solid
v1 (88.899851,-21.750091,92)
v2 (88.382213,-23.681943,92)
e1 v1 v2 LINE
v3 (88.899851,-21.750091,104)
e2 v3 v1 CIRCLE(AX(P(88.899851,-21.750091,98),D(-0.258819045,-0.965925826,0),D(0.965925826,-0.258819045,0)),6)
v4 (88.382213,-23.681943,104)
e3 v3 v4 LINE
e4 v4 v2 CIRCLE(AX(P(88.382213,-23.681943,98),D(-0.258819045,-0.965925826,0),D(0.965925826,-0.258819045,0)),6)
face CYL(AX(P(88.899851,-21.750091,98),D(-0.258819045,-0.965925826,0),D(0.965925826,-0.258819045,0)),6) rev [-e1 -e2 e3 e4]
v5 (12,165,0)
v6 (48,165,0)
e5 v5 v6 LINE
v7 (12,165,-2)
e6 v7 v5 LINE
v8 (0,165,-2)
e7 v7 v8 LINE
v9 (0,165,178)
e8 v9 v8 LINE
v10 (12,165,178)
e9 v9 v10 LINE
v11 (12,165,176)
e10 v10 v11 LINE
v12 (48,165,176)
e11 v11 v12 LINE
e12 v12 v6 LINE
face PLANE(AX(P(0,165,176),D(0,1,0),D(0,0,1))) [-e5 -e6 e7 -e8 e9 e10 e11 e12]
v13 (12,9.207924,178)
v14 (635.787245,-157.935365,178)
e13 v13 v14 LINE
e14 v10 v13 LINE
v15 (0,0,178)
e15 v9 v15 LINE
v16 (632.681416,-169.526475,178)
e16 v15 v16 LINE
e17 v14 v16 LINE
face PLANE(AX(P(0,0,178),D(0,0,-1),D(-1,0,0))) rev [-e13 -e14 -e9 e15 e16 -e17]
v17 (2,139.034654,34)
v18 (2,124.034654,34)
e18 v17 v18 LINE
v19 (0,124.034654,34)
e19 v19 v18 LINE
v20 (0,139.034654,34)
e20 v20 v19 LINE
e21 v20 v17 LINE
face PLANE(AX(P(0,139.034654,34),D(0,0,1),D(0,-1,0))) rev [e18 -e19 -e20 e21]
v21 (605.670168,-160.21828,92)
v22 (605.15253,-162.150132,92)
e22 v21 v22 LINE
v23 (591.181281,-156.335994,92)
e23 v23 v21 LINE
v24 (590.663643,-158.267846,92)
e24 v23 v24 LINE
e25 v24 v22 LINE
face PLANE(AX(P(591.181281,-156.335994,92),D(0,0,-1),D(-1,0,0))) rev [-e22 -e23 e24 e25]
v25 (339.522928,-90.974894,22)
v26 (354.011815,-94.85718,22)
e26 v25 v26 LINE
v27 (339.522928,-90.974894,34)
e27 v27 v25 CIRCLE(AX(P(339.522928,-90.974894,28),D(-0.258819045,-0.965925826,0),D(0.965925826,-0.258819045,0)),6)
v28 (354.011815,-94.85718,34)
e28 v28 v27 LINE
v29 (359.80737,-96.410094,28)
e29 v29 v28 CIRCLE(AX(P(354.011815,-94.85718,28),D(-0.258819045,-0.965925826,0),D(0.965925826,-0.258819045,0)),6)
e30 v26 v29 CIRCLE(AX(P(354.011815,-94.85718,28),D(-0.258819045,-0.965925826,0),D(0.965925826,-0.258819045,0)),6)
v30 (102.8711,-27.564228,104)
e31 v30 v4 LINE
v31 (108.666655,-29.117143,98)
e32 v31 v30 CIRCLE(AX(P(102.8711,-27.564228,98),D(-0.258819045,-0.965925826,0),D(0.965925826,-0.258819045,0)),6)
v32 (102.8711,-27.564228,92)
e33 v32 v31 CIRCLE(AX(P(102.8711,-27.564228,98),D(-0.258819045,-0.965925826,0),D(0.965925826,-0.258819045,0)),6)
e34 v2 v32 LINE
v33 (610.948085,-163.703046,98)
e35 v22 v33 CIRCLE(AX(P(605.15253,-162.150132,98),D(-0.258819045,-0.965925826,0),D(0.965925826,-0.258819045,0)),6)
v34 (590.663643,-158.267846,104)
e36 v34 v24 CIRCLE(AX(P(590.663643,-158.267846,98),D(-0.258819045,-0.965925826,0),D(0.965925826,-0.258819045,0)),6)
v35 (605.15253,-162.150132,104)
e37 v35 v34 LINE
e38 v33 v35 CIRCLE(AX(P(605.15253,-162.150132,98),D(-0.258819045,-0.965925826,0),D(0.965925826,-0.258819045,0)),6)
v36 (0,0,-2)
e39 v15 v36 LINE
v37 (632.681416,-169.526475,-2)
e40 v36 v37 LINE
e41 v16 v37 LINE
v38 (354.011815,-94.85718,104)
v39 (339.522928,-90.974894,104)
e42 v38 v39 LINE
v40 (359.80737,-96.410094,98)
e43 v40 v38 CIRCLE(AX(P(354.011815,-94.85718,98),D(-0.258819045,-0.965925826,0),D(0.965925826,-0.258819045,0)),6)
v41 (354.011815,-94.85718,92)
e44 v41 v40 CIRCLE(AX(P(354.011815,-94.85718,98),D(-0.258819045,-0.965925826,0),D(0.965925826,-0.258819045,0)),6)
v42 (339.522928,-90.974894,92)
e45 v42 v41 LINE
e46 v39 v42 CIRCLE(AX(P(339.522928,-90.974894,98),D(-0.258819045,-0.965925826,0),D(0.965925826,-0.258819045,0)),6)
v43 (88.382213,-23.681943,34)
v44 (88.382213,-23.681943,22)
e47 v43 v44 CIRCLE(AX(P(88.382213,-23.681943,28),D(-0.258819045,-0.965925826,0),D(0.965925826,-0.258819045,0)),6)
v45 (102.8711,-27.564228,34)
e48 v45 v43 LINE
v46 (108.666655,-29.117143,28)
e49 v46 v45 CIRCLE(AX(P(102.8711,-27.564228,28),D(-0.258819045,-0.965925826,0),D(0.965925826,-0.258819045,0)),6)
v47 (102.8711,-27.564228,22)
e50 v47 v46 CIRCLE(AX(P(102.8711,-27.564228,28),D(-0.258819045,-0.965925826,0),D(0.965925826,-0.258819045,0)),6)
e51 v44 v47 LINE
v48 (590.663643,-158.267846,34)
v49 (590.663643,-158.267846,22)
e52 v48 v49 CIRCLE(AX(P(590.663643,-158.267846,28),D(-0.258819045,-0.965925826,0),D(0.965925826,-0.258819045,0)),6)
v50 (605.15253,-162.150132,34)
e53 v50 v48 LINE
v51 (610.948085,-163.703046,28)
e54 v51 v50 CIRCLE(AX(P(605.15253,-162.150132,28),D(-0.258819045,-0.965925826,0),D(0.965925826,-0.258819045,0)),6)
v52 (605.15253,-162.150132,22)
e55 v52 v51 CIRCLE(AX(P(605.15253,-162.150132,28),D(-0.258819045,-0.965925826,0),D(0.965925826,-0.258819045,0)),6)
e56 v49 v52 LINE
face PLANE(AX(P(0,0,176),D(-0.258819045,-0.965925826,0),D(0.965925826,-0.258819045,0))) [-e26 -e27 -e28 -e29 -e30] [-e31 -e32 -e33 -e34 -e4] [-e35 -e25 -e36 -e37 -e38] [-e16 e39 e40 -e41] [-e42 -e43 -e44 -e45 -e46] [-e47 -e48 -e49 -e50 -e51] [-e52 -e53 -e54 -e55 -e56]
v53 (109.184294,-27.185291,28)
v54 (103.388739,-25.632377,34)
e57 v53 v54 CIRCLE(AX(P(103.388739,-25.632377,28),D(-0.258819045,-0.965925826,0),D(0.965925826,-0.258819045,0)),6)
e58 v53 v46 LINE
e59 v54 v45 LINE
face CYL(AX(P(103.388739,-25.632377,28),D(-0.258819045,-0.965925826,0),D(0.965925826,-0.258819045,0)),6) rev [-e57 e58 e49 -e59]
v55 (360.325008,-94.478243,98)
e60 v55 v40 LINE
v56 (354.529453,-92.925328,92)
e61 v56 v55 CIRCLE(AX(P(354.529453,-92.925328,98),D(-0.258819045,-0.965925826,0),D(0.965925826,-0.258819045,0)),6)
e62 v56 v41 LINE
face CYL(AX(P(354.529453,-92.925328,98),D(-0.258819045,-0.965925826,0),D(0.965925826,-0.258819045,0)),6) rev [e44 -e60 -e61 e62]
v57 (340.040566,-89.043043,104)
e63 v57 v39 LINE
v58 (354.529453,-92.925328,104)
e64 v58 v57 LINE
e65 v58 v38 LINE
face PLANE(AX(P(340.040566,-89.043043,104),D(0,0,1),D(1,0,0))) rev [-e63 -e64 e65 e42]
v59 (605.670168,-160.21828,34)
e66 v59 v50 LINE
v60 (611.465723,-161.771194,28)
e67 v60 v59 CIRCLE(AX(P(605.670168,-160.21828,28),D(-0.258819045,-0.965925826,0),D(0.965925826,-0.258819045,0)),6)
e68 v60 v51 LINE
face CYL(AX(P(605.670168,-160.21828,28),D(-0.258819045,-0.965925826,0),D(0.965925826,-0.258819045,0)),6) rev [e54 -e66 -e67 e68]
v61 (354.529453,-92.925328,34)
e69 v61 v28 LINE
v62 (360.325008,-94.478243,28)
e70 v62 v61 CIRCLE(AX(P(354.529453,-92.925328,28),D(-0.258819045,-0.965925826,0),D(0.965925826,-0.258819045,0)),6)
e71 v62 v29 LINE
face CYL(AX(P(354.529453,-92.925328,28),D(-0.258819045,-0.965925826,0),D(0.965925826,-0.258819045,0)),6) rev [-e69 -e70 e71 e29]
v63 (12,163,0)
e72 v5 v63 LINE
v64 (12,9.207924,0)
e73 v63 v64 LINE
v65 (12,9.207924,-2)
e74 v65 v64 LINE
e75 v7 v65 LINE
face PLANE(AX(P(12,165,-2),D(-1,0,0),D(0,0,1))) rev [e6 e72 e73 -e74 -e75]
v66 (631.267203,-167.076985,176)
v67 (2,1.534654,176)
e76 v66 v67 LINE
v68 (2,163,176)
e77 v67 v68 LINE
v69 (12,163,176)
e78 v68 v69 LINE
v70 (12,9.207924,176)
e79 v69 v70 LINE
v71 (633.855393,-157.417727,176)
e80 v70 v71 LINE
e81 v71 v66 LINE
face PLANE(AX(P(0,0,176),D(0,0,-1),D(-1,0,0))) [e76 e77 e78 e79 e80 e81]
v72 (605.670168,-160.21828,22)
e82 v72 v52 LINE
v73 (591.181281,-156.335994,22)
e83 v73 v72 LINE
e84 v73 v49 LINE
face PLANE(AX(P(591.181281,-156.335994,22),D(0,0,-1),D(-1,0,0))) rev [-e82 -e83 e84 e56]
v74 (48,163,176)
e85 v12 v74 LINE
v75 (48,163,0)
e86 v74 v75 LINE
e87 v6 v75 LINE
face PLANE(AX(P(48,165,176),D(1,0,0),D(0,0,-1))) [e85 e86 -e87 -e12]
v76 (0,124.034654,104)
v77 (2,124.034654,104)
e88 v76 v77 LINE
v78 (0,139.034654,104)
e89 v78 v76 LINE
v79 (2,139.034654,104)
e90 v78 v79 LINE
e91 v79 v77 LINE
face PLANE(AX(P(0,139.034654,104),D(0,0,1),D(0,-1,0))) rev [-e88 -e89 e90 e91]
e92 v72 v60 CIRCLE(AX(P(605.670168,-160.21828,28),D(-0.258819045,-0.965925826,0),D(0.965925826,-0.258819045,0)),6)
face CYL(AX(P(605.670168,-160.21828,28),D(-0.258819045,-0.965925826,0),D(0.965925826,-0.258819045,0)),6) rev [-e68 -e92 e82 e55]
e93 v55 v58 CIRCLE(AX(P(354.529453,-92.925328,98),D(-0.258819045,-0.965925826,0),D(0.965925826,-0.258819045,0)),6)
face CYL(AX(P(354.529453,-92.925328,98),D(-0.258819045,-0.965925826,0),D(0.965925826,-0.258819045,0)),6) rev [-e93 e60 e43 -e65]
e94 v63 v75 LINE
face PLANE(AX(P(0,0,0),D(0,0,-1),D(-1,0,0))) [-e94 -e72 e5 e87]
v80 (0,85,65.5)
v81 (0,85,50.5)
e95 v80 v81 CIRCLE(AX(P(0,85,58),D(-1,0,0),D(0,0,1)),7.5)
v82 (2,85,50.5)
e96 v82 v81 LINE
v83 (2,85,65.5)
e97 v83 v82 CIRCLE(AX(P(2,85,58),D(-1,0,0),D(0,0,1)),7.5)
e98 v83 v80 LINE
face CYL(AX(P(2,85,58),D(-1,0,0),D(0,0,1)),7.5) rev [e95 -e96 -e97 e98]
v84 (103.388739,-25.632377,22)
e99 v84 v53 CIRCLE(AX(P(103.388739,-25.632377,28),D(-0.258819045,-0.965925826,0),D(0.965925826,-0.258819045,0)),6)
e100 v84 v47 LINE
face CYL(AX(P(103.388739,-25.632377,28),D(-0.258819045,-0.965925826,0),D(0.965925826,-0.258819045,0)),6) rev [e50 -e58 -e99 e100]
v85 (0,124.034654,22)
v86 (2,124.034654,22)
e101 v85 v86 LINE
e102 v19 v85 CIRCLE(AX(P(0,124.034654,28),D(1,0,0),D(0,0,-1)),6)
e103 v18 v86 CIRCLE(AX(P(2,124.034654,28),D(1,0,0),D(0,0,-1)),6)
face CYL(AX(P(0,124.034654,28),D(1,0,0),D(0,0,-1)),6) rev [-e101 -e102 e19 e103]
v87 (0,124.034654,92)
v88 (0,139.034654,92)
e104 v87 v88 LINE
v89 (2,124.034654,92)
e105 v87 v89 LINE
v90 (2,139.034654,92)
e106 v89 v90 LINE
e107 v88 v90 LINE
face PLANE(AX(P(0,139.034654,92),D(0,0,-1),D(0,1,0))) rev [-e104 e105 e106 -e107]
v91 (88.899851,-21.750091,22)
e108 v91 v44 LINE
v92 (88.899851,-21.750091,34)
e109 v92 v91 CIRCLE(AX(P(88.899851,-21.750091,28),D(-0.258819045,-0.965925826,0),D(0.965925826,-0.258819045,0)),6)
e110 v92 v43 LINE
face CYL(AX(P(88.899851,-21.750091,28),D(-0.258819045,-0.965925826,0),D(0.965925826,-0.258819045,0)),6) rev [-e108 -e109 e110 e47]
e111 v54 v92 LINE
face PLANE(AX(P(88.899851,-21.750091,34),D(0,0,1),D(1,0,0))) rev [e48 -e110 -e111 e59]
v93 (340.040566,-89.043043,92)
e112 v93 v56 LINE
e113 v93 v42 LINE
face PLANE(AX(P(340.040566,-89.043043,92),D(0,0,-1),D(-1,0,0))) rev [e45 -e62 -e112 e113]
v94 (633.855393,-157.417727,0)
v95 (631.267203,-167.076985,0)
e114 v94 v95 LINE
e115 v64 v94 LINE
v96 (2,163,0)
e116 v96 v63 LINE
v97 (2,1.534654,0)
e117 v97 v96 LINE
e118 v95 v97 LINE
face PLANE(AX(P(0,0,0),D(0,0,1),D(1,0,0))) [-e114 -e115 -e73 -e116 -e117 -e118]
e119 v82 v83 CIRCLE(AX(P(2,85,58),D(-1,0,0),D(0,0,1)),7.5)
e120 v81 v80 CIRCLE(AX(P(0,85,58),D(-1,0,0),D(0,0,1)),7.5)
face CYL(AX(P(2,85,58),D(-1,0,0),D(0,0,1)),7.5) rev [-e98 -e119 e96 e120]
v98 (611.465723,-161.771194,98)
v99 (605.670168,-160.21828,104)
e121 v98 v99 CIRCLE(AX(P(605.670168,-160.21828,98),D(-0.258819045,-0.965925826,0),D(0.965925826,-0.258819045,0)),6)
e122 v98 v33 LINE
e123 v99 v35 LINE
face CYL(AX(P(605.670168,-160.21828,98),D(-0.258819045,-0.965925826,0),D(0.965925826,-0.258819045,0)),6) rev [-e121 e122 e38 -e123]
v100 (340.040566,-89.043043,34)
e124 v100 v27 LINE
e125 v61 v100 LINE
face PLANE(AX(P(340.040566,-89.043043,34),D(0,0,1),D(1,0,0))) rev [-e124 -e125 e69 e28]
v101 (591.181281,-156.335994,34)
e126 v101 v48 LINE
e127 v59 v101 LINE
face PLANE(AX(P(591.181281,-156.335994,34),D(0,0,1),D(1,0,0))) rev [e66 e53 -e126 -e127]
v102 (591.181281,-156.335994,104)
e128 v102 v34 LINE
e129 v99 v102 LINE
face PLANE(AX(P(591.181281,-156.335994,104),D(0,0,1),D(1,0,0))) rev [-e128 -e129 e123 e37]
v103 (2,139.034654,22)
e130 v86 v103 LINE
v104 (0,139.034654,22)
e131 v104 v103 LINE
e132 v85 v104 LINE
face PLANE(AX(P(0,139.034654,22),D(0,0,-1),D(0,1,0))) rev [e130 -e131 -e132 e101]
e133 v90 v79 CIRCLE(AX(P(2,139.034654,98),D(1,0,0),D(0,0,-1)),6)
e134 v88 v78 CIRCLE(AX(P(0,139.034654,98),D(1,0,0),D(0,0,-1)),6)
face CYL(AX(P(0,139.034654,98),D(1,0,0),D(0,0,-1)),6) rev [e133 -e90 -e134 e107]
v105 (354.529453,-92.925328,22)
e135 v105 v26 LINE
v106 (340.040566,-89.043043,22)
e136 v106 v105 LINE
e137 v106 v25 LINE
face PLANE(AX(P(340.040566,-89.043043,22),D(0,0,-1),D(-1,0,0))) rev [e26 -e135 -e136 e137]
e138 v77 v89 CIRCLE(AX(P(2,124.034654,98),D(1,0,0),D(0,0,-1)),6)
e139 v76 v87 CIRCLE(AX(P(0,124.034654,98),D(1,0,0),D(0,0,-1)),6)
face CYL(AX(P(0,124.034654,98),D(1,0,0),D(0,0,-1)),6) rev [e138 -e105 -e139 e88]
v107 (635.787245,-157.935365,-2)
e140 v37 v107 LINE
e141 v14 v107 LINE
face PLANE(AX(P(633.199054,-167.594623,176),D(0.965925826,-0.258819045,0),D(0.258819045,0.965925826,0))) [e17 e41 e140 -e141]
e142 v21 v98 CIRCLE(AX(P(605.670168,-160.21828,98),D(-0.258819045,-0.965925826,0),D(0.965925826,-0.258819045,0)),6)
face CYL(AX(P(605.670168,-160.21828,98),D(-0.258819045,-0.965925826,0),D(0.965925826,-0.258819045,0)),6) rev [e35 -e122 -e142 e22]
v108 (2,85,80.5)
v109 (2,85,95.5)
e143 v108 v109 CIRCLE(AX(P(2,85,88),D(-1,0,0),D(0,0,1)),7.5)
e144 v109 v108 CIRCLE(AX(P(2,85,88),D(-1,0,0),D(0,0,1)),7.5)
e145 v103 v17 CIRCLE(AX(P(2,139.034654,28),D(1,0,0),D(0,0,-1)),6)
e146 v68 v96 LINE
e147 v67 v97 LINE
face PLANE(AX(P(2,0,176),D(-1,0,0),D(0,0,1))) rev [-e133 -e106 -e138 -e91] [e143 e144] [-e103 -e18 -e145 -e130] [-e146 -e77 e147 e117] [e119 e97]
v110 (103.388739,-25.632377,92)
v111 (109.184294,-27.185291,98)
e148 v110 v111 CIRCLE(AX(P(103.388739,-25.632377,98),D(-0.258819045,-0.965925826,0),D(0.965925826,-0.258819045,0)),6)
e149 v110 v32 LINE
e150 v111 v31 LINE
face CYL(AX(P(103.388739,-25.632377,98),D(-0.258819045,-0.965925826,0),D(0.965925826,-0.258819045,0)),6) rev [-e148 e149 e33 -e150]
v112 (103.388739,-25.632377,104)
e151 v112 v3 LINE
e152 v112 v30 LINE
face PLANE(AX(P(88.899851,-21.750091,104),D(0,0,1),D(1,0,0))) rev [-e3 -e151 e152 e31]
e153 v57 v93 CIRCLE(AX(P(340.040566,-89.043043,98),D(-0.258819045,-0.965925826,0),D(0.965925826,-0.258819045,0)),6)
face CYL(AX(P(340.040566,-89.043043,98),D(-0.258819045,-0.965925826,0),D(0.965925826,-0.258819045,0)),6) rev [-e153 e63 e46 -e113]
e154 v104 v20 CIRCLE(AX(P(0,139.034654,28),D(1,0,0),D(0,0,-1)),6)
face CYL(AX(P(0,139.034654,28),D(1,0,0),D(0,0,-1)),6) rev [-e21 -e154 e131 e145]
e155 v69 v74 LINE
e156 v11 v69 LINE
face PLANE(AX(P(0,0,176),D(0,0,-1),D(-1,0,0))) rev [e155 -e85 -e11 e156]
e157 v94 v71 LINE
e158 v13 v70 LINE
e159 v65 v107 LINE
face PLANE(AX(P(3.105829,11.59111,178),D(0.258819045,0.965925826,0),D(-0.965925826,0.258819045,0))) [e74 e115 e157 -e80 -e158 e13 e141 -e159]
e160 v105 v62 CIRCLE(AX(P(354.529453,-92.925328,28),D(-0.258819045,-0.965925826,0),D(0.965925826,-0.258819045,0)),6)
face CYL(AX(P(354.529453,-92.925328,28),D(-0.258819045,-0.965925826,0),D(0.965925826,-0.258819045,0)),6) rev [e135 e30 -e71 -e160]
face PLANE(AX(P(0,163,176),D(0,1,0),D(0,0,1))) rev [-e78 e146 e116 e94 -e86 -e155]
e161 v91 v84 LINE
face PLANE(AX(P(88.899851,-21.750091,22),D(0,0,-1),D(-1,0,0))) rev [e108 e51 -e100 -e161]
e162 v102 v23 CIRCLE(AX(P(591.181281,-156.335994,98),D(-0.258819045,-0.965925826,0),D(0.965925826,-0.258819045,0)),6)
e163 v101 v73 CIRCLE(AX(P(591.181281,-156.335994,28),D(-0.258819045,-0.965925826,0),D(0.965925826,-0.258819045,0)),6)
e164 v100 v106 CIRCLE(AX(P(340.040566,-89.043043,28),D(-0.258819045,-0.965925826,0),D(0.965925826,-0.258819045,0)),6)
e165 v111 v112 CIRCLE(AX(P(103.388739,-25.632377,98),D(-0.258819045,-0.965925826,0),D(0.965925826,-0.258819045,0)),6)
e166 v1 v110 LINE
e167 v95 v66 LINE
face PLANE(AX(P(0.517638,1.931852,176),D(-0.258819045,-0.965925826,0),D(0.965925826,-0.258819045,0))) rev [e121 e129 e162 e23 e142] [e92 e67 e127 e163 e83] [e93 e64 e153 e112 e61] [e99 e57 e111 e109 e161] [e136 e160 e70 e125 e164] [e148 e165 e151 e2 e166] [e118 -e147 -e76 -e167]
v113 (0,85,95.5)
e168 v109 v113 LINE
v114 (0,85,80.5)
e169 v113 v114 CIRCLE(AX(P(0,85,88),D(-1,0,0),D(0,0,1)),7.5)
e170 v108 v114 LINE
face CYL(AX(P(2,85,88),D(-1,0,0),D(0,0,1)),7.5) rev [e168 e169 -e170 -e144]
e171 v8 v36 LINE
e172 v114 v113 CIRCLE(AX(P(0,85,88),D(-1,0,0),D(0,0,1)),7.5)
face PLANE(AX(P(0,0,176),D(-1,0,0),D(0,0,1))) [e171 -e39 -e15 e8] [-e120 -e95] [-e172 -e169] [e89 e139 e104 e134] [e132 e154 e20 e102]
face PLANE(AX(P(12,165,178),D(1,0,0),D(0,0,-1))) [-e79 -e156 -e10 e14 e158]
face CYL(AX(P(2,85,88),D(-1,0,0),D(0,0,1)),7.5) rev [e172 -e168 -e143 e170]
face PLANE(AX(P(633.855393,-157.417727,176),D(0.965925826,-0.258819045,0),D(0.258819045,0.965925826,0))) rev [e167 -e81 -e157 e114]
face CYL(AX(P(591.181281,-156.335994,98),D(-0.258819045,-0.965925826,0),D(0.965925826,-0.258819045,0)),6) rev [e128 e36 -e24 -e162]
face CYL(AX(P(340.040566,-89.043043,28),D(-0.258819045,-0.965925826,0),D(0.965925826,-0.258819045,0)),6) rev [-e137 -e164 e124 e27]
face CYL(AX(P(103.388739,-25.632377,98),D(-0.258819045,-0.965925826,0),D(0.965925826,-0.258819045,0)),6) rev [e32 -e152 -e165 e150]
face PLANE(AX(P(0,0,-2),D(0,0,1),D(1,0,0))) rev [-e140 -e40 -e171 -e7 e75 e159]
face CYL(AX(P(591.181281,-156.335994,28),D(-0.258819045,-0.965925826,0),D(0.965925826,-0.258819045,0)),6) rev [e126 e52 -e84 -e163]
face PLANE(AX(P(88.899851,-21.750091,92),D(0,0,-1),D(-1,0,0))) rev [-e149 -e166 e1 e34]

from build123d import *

# Parameters (mm, degrees)
EXTRUDE_THIN1_DEPTH  = 176
EXTRUDE_THIN2_DEPTH  = 2
EXTRUDE_THIN3_DEPTH  = 2
SKETCH4_W            = 2
SKETCH4_H            = 176
BOSS_EXTRUDE1_DEPTH  = 10
CUT_EXTRUDE1_DEPTH   = 2
LPATTERN1_COUNT      = 3
LPATTERN1_PITCH      = 260
LPATTERN1_COUNT_DIR2 = 2
LPATTERN1_PITCH_DIR2 = 70
CUT_EXTRUDE2_DEPTH   = 2
LPATTERN2_COUNT      = 2
LPATTERN2_PITCH      = 70
SKETCH7_R            = 7.5
CUT_EXTRUDE3_DEPTH   = 2
LPATTERN3_COUNT      = 2
LPATTERN3_PITCH      = 30


with BuildPart() as part:
    # Sketch1 → Extrude-Thin1 (new body)
    with BuildSketch(Plane.XY):
        Polygon((632.681416219, -169.526474542), (0, 0), (0, 165), (48, 165), (48, 163), (2, 163), (2, 1.534653976), (633.19905431, -167.59462289), align=None)
    extrude(amount=EXTRUDE_THIN1_DEPTH)

    # Sketch2 → Extrude-Thin2 (add)
    with BuildSketch(Plane.XY.offset(176)):
        Polygon((0, 165), (0, 0), (632.681416219, -169.526474542), (635.787244761, -157.935364627), (12, 9.207923856), (12, 165), align=None)
    extrude(amount=EXTRUDE_THIN2_DEPTH)

    # Sketch3 → Extrude-Thin3 (add)
    with BuildSketch(Plane(origin=(0, 0, 0), x_dir=(-1, 0, 0), z_dir=(0, 0, -1))):
        Polygon((0, 165), (0, 0), (-632.681416219, -169.526474542), (-635.787244761, -157.935364627), (-12, 9.207923856), (-12, 165), align=None)
    extrude(amount=EXTRUDE_THIN3_DEPTH)

    # Sketch4 → Boss-Extrude1 (add)
    with BuildSketch(Plane(origin=(0.51763809, 1.931851653, 0), x_dir=(0.9659258262890673, -0.25881904510252474, 0), z_dir=(0.25881904510252474, 0.9659258262890673, 0))):
        with Locations((654, -88)):
            Rectangle(SKETCH4_W, SKETCH4_H)
    extrude(amount=BOSS_EXTRUDE1_DEPTH)

    # Sketch5 → Cut-Extrude1 (cut)
    with BuildSketch(Plane(origin=(0, 0, 0), x_dir=(0.9659258262890673, -0.2588190451025247, 0), z_dir=(-0.2588190451025247, -0.9659258262890673, 0))):
        with BuildLine():
            Line((611.5, 34), (626.5, 34))
            ThreePointArc((626.5, 34), (632.5, 28), (626.5, 22))
            Line((626.5, 22), (611.5, 22))
            ThreePointArc((611.5, 22), (605.5, 28), (611.5, 34))
        make_face()
    cut_extrude1 = extrude(amount=-CUT_EXTRUDE1_DEPTH, mode=Mode.SUBTRACT)

    # LPattern1: Cut-Extrude1 3 × 2
    with Locations(*[Vector(-0.9659258262890673, 0.2588190451025247, 0) * (i * LPATTERN1_PITCH) + Vector(0, 0, 1) * (j * LPATTERN1_PITCH_DIR2) for i in range(LPATTERN1_COUNT) for j in range(LPATTERN1_COUNT_DIR2) if (i, j) != (0, 0)]):
        add(cut_extrude1, mode=Mode.SUBTRACT)

    # Sketch6 → Cut-Extrude2 (cut)
    with BuildSketch(Plane(origin=(2, 0, 0), x_dir=(0, 0, -1), z_dir=(1, 0, 0))):
        with BuildLine():
            Line((-22, 139.034653976), (-22, 124.034653976))
            ThreePointArc((-22, 124.034653976), (-28, 118.034653976), (-34, 124.034653976))
            Line((-34, 124.034653976), (-34, 139.034653976))
            ThreePointArc((-34, 139.034653976), (-28, 145.034653976), (-22, 139.034653976))
        make_face()
    cut_extrude2 = extrude(amount=-CUT_EXTRUDE2_DEPTH, mode=Mode.SUBTRACT)

    # LPattern2: Cut-Extrude2 ×2
    with Locations(*[(0, 0, i * LPATTERN2_PITCH) for i in range(1, LPATTERN2_COUNT)]):
        add(cut_extrude2, mode=Mode.SUBTRACT)

    # Sketch7 → Cut-Extrude3 (cut)
    with BuildSketch(Plane.ZY):
        with Locations((88, 85)):
            Circle(SKETCH7_R)
    cut_extrude3 = extrude(amount=-CUT_EXTRUDE3_DEPTH, mode=Mode.SUBTRACT)

    # LPattern3: Cut-Extrude3 ×2
    with Locations(*[(0, 0, -i * LPATTERN3_PITCH) for i in range(1, LPATTERN3_COUNT)]):
        add(cut_extrude3, mode=Mode.SUBTRACT)


solid = part.part
